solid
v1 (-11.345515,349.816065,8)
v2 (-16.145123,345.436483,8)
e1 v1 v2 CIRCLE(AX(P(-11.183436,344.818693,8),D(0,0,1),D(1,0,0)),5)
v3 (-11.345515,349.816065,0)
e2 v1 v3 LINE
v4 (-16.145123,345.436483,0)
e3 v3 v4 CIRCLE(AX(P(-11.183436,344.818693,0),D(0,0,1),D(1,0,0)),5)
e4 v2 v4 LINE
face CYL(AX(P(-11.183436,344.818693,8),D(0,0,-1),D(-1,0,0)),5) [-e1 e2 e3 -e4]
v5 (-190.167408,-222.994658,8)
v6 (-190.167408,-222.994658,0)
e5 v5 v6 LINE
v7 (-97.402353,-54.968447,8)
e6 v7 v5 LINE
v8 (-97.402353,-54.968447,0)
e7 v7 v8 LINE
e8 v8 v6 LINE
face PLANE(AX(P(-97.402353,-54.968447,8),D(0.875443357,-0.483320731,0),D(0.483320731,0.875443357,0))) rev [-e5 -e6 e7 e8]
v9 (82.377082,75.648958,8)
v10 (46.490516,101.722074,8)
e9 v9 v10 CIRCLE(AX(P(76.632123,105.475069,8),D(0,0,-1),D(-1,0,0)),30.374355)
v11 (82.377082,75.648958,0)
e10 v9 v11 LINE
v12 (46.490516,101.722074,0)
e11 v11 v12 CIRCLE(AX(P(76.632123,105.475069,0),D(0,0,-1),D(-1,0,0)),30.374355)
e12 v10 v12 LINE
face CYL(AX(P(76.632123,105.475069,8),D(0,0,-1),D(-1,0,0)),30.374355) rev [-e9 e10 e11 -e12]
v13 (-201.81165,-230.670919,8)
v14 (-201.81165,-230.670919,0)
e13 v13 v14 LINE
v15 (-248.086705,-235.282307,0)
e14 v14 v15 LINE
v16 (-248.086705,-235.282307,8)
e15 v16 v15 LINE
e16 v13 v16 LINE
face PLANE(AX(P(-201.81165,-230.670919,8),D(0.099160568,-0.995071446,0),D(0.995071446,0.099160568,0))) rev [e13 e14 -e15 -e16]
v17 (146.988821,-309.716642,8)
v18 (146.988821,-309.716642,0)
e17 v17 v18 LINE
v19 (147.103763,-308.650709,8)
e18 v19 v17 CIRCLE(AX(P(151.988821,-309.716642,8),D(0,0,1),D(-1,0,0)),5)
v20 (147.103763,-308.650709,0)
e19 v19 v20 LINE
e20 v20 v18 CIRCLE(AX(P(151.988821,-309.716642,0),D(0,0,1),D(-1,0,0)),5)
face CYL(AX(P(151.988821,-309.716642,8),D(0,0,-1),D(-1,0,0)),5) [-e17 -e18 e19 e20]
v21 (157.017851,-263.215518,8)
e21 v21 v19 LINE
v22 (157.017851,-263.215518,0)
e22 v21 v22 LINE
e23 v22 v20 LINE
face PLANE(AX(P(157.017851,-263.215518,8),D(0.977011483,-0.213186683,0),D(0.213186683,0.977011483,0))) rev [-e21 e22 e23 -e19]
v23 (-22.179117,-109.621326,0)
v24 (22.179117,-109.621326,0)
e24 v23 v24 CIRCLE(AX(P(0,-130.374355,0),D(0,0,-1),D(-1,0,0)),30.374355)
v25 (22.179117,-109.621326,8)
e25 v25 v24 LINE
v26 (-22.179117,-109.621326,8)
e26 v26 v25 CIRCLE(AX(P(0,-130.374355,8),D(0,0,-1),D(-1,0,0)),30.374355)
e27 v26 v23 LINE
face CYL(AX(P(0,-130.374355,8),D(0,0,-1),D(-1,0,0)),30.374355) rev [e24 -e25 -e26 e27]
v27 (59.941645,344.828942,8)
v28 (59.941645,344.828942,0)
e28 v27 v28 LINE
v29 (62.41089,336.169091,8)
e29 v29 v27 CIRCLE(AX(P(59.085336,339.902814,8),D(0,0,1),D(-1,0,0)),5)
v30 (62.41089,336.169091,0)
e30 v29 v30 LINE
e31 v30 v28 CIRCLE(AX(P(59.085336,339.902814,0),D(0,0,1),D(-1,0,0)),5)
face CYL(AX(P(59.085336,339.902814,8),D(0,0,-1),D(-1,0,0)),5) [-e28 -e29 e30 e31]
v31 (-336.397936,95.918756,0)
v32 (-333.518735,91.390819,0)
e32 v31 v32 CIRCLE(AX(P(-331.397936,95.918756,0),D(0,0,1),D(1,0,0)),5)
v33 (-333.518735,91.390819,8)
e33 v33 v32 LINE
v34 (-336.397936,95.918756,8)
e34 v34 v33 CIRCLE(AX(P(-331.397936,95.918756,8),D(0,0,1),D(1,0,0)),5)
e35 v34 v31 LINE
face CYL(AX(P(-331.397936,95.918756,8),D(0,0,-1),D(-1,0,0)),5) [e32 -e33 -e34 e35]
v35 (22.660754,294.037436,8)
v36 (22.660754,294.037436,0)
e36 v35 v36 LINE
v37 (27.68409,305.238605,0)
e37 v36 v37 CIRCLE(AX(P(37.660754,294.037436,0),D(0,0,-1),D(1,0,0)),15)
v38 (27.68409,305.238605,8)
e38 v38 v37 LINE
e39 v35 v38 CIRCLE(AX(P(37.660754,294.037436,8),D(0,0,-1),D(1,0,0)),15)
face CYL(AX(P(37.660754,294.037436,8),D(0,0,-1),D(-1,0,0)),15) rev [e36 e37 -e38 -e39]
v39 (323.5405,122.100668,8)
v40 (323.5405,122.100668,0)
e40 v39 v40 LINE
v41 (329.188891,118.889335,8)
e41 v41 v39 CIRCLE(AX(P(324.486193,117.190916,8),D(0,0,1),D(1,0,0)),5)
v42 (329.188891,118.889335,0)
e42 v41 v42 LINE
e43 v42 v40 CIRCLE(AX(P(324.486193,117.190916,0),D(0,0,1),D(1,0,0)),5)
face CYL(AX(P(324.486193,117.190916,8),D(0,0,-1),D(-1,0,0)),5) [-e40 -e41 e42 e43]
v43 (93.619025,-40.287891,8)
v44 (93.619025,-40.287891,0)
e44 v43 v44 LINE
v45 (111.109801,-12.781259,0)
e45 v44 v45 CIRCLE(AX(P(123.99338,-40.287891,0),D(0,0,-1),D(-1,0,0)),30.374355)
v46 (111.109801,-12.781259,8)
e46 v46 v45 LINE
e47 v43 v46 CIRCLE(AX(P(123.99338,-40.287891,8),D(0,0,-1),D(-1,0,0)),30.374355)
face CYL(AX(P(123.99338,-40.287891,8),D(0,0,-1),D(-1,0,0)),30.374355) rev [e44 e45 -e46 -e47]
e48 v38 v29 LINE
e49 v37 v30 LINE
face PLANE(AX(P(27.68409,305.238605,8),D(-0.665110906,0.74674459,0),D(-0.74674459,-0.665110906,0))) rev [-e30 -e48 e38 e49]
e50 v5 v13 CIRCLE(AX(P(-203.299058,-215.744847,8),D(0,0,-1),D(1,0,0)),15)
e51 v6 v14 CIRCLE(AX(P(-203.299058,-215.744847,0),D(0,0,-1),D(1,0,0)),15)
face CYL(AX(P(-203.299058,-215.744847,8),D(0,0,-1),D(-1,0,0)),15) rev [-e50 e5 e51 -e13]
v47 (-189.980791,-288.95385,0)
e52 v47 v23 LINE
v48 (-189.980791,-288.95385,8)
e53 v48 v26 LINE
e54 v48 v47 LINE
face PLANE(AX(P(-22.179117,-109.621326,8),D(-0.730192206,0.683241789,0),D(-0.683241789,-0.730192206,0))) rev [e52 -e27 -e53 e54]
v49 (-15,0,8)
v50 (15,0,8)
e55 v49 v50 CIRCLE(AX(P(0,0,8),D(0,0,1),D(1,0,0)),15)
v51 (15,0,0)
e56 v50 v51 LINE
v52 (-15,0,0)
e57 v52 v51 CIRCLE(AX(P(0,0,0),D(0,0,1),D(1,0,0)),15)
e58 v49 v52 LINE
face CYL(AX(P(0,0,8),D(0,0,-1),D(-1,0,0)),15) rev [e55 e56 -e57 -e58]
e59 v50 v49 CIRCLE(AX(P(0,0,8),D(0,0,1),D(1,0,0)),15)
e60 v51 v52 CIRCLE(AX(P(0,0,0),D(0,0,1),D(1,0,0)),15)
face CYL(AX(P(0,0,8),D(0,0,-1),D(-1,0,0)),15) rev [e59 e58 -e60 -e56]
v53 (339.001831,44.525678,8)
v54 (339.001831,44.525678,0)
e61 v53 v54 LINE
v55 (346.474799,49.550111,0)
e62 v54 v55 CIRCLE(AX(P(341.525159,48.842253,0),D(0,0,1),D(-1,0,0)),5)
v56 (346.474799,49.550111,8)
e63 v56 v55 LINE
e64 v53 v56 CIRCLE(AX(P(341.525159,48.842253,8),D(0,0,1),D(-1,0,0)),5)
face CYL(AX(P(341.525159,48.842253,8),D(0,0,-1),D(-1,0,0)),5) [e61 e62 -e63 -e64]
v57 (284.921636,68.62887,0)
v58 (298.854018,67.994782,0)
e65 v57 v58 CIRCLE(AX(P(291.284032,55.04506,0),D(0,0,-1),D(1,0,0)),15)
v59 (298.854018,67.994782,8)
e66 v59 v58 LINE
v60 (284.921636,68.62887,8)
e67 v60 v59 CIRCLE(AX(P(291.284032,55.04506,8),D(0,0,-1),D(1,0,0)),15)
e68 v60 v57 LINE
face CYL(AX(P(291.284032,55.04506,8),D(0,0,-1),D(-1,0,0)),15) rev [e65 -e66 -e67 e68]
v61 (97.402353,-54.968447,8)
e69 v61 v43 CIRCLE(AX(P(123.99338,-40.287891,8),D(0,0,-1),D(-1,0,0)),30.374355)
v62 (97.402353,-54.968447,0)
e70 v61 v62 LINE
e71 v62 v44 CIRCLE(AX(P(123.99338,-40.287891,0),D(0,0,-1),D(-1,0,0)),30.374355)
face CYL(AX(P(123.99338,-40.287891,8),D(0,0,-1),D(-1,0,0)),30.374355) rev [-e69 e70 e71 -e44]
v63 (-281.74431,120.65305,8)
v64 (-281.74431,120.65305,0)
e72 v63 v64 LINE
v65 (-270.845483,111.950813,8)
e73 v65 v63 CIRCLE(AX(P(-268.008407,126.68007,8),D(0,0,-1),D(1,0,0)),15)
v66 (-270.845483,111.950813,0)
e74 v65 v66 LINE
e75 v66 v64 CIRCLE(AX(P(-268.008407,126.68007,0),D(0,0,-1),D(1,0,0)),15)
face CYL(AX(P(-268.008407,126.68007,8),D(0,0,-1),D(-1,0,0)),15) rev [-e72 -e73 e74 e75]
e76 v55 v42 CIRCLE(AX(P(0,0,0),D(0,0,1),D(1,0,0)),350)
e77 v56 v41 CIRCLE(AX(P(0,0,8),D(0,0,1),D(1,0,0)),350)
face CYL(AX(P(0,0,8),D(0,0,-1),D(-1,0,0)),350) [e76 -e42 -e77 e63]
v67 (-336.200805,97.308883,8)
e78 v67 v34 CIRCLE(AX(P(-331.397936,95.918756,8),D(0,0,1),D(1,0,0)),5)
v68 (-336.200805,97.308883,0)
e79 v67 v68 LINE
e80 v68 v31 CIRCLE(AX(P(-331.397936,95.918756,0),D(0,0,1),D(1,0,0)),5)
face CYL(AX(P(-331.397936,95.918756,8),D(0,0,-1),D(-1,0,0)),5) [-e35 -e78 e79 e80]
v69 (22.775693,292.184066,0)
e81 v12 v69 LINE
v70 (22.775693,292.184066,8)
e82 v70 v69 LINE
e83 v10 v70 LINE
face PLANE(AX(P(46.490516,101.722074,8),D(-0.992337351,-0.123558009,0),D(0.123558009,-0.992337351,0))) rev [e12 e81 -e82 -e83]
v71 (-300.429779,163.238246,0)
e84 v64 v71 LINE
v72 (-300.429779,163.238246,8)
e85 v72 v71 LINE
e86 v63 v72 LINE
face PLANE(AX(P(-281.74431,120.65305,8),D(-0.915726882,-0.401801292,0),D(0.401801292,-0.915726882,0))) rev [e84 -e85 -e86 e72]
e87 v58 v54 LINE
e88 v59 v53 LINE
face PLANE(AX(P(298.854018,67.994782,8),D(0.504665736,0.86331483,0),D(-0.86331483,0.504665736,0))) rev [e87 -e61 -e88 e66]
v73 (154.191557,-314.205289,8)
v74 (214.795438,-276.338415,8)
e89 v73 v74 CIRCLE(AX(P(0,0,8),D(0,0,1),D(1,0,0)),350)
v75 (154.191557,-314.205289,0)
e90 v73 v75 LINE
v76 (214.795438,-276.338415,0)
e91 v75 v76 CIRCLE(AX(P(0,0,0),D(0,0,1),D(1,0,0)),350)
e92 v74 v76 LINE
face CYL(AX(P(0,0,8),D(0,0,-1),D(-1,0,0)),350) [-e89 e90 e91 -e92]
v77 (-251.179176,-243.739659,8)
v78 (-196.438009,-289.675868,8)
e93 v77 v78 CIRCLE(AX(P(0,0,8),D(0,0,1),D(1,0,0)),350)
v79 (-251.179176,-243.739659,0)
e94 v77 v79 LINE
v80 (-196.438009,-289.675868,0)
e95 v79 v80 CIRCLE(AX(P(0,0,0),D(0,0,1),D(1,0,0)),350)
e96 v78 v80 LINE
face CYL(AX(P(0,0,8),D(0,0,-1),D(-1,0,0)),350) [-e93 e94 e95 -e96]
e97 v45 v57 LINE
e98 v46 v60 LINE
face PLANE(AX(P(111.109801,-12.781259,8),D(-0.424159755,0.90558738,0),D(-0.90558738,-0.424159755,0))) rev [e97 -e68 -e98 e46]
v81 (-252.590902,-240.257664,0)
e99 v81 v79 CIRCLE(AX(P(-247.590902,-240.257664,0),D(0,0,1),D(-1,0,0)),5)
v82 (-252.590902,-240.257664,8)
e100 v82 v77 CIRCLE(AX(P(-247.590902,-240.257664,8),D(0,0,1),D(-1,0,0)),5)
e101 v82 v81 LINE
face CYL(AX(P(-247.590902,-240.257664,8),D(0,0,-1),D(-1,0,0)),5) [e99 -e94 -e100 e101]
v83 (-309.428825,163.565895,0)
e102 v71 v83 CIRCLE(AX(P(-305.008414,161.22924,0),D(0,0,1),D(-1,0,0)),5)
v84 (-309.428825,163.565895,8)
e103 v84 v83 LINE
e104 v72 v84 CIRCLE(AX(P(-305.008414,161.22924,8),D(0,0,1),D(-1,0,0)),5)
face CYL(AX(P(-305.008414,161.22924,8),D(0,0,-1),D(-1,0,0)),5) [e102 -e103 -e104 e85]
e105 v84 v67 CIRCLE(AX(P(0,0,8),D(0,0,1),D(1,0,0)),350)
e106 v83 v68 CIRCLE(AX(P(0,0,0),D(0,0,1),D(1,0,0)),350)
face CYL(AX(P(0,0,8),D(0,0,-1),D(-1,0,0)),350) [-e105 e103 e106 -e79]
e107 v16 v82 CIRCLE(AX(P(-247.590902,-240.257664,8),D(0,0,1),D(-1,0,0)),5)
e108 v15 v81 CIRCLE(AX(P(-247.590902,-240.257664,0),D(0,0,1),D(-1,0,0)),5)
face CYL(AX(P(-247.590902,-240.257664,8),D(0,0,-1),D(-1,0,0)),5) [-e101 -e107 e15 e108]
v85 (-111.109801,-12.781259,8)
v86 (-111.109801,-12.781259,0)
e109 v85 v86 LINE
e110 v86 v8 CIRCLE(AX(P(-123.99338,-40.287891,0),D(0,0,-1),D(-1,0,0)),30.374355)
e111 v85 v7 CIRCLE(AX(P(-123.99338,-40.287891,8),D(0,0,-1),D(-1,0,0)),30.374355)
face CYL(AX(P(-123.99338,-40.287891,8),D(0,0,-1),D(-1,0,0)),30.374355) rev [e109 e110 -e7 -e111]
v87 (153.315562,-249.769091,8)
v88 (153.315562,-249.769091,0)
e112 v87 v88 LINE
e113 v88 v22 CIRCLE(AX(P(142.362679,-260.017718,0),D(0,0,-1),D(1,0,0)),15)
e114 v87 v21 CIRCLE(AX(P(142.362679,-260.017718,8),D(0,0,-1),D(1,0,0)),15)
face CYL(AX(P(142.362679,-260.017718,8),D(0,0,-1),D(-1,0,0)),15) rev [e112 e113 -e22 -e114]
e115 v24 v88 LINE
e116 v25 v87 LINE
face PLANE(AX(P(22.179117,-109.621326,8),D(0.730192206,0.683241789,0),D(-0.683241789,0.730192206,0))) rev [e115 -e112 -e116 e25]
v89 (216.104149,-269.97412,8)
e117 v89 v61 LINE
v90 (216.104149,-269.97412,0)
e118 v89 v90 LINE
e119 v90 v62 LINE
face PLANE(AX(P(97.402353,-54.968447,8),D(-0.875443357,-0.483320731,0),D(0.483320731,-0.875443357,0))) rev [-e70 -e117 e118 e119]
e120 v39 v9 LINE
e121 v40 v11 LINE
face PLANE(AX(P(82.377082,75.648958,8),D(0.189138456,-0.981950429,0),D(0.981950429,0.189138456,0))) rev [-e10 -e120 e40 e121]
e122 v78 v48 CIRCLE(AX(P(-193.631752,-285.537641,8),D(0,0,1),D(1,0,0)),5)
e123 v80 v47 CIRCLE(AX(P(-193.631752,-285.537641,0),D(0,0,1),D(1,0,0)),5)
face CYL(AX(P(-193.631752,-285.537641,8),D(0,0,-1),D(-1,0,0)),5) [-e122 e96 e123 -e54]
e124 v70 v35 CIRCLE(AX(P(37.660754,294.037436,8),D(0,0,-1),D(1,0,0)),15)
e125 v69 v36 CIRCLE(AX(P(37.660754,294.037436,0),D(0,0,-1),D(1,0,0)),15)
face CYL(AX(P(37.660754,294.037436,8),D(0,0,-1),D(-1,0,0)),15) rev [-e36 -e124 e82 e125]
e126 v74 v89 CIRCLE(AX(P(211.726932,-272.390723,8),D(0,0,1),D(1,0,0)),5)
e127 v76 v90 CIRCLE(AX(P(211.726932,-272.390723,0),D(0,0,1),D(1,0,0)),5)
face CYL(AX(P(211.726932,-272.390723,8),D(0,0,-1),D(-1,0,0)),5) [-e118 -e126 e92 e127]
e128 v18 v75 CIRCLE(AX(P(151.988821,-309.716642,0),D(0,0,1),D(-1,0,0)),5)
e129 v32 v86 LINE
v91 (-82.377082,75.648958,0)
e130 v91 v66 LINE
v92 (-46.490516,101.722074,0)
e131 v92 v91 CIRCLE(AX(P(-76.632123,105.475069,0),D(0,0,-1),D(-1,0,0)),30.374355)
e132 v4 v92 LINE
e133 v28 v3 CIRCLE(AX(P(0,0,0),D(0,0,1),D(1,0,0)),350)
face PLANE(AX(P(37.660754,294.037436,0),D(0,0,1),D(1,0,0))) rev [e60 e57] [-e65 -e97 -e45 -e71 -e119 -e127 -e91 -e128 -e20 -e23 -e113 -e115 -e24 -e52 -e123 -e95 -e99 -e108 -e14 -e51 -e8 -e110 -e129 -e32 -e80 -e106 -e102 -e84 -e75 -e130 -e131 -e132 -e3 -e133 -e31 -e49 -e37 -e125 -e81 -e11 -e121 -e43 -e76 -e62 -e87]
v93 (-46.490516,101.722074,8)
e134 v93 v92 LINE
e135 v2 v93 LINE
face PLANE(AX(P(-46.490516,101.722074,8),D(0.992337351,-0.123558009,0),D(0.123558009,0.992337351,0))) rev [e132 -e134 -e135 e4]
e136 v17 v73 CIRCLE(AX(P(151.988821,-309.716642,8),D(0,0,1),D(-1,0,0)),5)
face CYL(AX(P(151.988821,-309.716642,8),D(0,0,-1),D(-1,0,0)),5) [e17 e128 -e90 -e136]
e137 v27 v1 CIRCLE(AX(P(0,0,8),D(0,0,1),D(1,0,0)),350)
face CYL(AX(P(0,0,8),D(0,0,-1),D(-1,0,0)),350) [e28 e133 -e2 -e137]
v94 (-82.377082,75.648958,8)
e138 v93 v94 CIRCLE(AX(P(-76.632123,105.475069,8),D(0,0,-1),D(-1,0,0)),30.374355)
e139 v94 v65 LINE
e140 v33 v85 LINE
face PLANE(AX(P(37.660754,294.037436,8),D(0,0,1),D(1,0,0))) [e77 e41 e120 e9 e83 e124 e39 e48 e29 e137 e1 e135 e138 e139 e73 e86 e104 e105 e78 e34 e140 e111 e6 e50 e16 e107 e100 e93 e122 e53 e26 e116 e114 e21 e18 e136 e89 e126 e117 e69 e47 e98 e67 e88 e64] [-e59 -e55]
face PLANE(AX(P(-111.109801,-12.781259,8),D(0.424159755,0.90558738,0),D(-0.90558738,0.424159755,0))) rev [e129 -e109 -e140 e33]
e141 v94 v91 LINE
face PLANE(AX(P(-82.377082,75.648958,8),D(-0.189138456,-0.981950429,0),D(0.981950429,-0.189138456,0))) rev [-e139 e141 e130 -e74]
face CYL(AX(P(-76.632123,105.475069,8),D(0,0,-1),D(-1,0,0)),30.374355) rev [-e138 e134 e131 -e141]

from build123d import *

# Parameters (mm, degrees)
SKETCH1_R               = 15
LINEAR_AUSTRAGEN1_DEPTH = 8


with BuildPart() as part:
    # Sketch1 → Linear austragen1 (new body)
    with BuildSketch(Plane.XY):
        with BuildLine():
            Line((-46.490516198, 101.722073941), (-16.145123023, 345.436482626))
            ThreePointArc((-16.145123023, 345.436482626), (-14.553663061, 348.512142372), (-11.345515054, 349.816064937))
            ThreePointArc((-11.345515054, 349.816064937), (24.425679263, 349.146654277), (59.941644882, 344.828941954))
            ThreePointArc((59.941644882, 344.828941954), (63.893687736, 341.27385411), (62.410890197, 336.16909126))
            Line((62.410890197, 336.16909126), (27.68409004, 305.238604713))
            ThreePointArc((27.68409004, 305.238604713), (23.620398385, 299.316491146), (22.775693358, 292.184065725))
            Line((22.775693358, 292.184065725), (46.490516198, 101.722073941))
            ThreePointArc((46.490516198, 101.722073941), (58.778525229, 80.901699437), (82.37708169, 75.648957927))
            Line((82.37708169, 75.648957927), (323.540500377, 122.100668066))
            ThreePointArc((323.540500377, 122.100668066), (326.957414795, 121.537530829), (329.188891102, 118.889334994))
            ThreePointArc((329.188891102, 118.889334994), (339.606150684, 84.662048273), (346.474799191, 49.550111254))
            ThreePointArc((346.474799191, 49.550111254), (344.314958136, 44.692912585), (339.001830525, 44.525678373))
            Line((339.001830525, 44.525678373), (298.854018333, 67.994781966))
            ThreePointArc((298.854018333, 67.994781966), (291.966003854, 70.02954866), (284.921635971, 68.628870213))
            Line((284.921635971, 68.628870213), (111.109800855, -12.781258825))
            ThreePointArc((111.109800855, -12.781258825), (95.10565163, -30.901699437), (97.402352577, -54.968446729))
            Line((97.402352577, -54.968446729), (216.104148993, -269.974119712))
            ThreePointArc((216.104148993, -269.974119712), (216.624458278, -273.397817411), (214.795438474, -276.338415011))
            ThreePointArc((214.795438474, -276.338415011), (185.462464648, -296.822630887), (154.191557264, -314.205289052))
            ThreePointArc((154.191557264, -314.205289052), (148.904659228, -313.652115076), (147.103763315, -308.650708653))
            Line((147.103763315, -308.650708653), (157.017850965, -263.215518401))
            ThreePointArc((157.017850965, -263.215518401), (156.824515556, -256.035849857), (153.315561803, -249.769091324))
            Line((153.315561803, -249.769091324), (22.179117214, -109.621326314))
            ThreePointArc((22.179117214, -109.621326314), (0, -100), (-22.179117214, -109.621326314))
            Line((-22.179117214, -109.621326314), (-189.980791189, -288.953850131))
            ThreePointArc((-189.980791189, -288.953850131), (-193.076136784, -290.506674439), (-196.438009496, -289.675867868))
            ThreePointArc((-196.438009496, -289.675867868), (-224.984043894, -268.108522791), (-251.179176024, -243.739659333))
            ThreePointArc((-251.179176024, -243.739659333), (-252.28681765, -238.540580345), (-248.086704923, -235.282306972))
            Line((-248.086704923, -235.282306972), (-201.811649597, -230.670918704))
            ThreePointArc((-201.811649597, -230.670918704), (-195.043122971, -228.26840621), (-190.167407773, -222.99465799))
            Line((-190.167407773, -222.99465799), (-97.402352577, -54.968446729))
            ThreePointArc((-97.402352577, -54.968446729), (-95.10565163, -30.901699437), (-111.109800855, -12.781258825))
            Line((-111.109800855, -12.781258825), (-333.518735158, 91.390819151))
            ThreePointArc((-333.518735158, 91.390819151), (-335.952073227, 93.854818649), (-336.200805025, 97.308882948))
            ThreePointArc((-336.200805025, 97.308882948), (-324.510250701, 131.122451129), (-309.428825313, 163.565895178))
            ThreePointArc((-309.428825313, 163.565895178), (-304.826487449, 166.225928727), (-300.429779115, 163.238245993))
            Line((-300.429779115, 163.238245993), (-281.744309741, 120.653050426))
            ThreePointArc((-281.744309741, 120.653050426), (-277.367794824, 114.958216262), (-270.845483359, 111.950813376))
            Line((-270.845483359, 111.950813376), (-82.37708169, 75.648957927))
            ThreePointArc((-82.37708169, 75.648957927), (-58.778525229, 80.901699437), (-46.490516198, 101.722073941))
        make_face()
        Circle(SKETCH1_R, mode=Mode.SUBTRACT)
    extrude(amount=LINEAR_AUSTRAGEN1_DEPTH)


solid = part.part
